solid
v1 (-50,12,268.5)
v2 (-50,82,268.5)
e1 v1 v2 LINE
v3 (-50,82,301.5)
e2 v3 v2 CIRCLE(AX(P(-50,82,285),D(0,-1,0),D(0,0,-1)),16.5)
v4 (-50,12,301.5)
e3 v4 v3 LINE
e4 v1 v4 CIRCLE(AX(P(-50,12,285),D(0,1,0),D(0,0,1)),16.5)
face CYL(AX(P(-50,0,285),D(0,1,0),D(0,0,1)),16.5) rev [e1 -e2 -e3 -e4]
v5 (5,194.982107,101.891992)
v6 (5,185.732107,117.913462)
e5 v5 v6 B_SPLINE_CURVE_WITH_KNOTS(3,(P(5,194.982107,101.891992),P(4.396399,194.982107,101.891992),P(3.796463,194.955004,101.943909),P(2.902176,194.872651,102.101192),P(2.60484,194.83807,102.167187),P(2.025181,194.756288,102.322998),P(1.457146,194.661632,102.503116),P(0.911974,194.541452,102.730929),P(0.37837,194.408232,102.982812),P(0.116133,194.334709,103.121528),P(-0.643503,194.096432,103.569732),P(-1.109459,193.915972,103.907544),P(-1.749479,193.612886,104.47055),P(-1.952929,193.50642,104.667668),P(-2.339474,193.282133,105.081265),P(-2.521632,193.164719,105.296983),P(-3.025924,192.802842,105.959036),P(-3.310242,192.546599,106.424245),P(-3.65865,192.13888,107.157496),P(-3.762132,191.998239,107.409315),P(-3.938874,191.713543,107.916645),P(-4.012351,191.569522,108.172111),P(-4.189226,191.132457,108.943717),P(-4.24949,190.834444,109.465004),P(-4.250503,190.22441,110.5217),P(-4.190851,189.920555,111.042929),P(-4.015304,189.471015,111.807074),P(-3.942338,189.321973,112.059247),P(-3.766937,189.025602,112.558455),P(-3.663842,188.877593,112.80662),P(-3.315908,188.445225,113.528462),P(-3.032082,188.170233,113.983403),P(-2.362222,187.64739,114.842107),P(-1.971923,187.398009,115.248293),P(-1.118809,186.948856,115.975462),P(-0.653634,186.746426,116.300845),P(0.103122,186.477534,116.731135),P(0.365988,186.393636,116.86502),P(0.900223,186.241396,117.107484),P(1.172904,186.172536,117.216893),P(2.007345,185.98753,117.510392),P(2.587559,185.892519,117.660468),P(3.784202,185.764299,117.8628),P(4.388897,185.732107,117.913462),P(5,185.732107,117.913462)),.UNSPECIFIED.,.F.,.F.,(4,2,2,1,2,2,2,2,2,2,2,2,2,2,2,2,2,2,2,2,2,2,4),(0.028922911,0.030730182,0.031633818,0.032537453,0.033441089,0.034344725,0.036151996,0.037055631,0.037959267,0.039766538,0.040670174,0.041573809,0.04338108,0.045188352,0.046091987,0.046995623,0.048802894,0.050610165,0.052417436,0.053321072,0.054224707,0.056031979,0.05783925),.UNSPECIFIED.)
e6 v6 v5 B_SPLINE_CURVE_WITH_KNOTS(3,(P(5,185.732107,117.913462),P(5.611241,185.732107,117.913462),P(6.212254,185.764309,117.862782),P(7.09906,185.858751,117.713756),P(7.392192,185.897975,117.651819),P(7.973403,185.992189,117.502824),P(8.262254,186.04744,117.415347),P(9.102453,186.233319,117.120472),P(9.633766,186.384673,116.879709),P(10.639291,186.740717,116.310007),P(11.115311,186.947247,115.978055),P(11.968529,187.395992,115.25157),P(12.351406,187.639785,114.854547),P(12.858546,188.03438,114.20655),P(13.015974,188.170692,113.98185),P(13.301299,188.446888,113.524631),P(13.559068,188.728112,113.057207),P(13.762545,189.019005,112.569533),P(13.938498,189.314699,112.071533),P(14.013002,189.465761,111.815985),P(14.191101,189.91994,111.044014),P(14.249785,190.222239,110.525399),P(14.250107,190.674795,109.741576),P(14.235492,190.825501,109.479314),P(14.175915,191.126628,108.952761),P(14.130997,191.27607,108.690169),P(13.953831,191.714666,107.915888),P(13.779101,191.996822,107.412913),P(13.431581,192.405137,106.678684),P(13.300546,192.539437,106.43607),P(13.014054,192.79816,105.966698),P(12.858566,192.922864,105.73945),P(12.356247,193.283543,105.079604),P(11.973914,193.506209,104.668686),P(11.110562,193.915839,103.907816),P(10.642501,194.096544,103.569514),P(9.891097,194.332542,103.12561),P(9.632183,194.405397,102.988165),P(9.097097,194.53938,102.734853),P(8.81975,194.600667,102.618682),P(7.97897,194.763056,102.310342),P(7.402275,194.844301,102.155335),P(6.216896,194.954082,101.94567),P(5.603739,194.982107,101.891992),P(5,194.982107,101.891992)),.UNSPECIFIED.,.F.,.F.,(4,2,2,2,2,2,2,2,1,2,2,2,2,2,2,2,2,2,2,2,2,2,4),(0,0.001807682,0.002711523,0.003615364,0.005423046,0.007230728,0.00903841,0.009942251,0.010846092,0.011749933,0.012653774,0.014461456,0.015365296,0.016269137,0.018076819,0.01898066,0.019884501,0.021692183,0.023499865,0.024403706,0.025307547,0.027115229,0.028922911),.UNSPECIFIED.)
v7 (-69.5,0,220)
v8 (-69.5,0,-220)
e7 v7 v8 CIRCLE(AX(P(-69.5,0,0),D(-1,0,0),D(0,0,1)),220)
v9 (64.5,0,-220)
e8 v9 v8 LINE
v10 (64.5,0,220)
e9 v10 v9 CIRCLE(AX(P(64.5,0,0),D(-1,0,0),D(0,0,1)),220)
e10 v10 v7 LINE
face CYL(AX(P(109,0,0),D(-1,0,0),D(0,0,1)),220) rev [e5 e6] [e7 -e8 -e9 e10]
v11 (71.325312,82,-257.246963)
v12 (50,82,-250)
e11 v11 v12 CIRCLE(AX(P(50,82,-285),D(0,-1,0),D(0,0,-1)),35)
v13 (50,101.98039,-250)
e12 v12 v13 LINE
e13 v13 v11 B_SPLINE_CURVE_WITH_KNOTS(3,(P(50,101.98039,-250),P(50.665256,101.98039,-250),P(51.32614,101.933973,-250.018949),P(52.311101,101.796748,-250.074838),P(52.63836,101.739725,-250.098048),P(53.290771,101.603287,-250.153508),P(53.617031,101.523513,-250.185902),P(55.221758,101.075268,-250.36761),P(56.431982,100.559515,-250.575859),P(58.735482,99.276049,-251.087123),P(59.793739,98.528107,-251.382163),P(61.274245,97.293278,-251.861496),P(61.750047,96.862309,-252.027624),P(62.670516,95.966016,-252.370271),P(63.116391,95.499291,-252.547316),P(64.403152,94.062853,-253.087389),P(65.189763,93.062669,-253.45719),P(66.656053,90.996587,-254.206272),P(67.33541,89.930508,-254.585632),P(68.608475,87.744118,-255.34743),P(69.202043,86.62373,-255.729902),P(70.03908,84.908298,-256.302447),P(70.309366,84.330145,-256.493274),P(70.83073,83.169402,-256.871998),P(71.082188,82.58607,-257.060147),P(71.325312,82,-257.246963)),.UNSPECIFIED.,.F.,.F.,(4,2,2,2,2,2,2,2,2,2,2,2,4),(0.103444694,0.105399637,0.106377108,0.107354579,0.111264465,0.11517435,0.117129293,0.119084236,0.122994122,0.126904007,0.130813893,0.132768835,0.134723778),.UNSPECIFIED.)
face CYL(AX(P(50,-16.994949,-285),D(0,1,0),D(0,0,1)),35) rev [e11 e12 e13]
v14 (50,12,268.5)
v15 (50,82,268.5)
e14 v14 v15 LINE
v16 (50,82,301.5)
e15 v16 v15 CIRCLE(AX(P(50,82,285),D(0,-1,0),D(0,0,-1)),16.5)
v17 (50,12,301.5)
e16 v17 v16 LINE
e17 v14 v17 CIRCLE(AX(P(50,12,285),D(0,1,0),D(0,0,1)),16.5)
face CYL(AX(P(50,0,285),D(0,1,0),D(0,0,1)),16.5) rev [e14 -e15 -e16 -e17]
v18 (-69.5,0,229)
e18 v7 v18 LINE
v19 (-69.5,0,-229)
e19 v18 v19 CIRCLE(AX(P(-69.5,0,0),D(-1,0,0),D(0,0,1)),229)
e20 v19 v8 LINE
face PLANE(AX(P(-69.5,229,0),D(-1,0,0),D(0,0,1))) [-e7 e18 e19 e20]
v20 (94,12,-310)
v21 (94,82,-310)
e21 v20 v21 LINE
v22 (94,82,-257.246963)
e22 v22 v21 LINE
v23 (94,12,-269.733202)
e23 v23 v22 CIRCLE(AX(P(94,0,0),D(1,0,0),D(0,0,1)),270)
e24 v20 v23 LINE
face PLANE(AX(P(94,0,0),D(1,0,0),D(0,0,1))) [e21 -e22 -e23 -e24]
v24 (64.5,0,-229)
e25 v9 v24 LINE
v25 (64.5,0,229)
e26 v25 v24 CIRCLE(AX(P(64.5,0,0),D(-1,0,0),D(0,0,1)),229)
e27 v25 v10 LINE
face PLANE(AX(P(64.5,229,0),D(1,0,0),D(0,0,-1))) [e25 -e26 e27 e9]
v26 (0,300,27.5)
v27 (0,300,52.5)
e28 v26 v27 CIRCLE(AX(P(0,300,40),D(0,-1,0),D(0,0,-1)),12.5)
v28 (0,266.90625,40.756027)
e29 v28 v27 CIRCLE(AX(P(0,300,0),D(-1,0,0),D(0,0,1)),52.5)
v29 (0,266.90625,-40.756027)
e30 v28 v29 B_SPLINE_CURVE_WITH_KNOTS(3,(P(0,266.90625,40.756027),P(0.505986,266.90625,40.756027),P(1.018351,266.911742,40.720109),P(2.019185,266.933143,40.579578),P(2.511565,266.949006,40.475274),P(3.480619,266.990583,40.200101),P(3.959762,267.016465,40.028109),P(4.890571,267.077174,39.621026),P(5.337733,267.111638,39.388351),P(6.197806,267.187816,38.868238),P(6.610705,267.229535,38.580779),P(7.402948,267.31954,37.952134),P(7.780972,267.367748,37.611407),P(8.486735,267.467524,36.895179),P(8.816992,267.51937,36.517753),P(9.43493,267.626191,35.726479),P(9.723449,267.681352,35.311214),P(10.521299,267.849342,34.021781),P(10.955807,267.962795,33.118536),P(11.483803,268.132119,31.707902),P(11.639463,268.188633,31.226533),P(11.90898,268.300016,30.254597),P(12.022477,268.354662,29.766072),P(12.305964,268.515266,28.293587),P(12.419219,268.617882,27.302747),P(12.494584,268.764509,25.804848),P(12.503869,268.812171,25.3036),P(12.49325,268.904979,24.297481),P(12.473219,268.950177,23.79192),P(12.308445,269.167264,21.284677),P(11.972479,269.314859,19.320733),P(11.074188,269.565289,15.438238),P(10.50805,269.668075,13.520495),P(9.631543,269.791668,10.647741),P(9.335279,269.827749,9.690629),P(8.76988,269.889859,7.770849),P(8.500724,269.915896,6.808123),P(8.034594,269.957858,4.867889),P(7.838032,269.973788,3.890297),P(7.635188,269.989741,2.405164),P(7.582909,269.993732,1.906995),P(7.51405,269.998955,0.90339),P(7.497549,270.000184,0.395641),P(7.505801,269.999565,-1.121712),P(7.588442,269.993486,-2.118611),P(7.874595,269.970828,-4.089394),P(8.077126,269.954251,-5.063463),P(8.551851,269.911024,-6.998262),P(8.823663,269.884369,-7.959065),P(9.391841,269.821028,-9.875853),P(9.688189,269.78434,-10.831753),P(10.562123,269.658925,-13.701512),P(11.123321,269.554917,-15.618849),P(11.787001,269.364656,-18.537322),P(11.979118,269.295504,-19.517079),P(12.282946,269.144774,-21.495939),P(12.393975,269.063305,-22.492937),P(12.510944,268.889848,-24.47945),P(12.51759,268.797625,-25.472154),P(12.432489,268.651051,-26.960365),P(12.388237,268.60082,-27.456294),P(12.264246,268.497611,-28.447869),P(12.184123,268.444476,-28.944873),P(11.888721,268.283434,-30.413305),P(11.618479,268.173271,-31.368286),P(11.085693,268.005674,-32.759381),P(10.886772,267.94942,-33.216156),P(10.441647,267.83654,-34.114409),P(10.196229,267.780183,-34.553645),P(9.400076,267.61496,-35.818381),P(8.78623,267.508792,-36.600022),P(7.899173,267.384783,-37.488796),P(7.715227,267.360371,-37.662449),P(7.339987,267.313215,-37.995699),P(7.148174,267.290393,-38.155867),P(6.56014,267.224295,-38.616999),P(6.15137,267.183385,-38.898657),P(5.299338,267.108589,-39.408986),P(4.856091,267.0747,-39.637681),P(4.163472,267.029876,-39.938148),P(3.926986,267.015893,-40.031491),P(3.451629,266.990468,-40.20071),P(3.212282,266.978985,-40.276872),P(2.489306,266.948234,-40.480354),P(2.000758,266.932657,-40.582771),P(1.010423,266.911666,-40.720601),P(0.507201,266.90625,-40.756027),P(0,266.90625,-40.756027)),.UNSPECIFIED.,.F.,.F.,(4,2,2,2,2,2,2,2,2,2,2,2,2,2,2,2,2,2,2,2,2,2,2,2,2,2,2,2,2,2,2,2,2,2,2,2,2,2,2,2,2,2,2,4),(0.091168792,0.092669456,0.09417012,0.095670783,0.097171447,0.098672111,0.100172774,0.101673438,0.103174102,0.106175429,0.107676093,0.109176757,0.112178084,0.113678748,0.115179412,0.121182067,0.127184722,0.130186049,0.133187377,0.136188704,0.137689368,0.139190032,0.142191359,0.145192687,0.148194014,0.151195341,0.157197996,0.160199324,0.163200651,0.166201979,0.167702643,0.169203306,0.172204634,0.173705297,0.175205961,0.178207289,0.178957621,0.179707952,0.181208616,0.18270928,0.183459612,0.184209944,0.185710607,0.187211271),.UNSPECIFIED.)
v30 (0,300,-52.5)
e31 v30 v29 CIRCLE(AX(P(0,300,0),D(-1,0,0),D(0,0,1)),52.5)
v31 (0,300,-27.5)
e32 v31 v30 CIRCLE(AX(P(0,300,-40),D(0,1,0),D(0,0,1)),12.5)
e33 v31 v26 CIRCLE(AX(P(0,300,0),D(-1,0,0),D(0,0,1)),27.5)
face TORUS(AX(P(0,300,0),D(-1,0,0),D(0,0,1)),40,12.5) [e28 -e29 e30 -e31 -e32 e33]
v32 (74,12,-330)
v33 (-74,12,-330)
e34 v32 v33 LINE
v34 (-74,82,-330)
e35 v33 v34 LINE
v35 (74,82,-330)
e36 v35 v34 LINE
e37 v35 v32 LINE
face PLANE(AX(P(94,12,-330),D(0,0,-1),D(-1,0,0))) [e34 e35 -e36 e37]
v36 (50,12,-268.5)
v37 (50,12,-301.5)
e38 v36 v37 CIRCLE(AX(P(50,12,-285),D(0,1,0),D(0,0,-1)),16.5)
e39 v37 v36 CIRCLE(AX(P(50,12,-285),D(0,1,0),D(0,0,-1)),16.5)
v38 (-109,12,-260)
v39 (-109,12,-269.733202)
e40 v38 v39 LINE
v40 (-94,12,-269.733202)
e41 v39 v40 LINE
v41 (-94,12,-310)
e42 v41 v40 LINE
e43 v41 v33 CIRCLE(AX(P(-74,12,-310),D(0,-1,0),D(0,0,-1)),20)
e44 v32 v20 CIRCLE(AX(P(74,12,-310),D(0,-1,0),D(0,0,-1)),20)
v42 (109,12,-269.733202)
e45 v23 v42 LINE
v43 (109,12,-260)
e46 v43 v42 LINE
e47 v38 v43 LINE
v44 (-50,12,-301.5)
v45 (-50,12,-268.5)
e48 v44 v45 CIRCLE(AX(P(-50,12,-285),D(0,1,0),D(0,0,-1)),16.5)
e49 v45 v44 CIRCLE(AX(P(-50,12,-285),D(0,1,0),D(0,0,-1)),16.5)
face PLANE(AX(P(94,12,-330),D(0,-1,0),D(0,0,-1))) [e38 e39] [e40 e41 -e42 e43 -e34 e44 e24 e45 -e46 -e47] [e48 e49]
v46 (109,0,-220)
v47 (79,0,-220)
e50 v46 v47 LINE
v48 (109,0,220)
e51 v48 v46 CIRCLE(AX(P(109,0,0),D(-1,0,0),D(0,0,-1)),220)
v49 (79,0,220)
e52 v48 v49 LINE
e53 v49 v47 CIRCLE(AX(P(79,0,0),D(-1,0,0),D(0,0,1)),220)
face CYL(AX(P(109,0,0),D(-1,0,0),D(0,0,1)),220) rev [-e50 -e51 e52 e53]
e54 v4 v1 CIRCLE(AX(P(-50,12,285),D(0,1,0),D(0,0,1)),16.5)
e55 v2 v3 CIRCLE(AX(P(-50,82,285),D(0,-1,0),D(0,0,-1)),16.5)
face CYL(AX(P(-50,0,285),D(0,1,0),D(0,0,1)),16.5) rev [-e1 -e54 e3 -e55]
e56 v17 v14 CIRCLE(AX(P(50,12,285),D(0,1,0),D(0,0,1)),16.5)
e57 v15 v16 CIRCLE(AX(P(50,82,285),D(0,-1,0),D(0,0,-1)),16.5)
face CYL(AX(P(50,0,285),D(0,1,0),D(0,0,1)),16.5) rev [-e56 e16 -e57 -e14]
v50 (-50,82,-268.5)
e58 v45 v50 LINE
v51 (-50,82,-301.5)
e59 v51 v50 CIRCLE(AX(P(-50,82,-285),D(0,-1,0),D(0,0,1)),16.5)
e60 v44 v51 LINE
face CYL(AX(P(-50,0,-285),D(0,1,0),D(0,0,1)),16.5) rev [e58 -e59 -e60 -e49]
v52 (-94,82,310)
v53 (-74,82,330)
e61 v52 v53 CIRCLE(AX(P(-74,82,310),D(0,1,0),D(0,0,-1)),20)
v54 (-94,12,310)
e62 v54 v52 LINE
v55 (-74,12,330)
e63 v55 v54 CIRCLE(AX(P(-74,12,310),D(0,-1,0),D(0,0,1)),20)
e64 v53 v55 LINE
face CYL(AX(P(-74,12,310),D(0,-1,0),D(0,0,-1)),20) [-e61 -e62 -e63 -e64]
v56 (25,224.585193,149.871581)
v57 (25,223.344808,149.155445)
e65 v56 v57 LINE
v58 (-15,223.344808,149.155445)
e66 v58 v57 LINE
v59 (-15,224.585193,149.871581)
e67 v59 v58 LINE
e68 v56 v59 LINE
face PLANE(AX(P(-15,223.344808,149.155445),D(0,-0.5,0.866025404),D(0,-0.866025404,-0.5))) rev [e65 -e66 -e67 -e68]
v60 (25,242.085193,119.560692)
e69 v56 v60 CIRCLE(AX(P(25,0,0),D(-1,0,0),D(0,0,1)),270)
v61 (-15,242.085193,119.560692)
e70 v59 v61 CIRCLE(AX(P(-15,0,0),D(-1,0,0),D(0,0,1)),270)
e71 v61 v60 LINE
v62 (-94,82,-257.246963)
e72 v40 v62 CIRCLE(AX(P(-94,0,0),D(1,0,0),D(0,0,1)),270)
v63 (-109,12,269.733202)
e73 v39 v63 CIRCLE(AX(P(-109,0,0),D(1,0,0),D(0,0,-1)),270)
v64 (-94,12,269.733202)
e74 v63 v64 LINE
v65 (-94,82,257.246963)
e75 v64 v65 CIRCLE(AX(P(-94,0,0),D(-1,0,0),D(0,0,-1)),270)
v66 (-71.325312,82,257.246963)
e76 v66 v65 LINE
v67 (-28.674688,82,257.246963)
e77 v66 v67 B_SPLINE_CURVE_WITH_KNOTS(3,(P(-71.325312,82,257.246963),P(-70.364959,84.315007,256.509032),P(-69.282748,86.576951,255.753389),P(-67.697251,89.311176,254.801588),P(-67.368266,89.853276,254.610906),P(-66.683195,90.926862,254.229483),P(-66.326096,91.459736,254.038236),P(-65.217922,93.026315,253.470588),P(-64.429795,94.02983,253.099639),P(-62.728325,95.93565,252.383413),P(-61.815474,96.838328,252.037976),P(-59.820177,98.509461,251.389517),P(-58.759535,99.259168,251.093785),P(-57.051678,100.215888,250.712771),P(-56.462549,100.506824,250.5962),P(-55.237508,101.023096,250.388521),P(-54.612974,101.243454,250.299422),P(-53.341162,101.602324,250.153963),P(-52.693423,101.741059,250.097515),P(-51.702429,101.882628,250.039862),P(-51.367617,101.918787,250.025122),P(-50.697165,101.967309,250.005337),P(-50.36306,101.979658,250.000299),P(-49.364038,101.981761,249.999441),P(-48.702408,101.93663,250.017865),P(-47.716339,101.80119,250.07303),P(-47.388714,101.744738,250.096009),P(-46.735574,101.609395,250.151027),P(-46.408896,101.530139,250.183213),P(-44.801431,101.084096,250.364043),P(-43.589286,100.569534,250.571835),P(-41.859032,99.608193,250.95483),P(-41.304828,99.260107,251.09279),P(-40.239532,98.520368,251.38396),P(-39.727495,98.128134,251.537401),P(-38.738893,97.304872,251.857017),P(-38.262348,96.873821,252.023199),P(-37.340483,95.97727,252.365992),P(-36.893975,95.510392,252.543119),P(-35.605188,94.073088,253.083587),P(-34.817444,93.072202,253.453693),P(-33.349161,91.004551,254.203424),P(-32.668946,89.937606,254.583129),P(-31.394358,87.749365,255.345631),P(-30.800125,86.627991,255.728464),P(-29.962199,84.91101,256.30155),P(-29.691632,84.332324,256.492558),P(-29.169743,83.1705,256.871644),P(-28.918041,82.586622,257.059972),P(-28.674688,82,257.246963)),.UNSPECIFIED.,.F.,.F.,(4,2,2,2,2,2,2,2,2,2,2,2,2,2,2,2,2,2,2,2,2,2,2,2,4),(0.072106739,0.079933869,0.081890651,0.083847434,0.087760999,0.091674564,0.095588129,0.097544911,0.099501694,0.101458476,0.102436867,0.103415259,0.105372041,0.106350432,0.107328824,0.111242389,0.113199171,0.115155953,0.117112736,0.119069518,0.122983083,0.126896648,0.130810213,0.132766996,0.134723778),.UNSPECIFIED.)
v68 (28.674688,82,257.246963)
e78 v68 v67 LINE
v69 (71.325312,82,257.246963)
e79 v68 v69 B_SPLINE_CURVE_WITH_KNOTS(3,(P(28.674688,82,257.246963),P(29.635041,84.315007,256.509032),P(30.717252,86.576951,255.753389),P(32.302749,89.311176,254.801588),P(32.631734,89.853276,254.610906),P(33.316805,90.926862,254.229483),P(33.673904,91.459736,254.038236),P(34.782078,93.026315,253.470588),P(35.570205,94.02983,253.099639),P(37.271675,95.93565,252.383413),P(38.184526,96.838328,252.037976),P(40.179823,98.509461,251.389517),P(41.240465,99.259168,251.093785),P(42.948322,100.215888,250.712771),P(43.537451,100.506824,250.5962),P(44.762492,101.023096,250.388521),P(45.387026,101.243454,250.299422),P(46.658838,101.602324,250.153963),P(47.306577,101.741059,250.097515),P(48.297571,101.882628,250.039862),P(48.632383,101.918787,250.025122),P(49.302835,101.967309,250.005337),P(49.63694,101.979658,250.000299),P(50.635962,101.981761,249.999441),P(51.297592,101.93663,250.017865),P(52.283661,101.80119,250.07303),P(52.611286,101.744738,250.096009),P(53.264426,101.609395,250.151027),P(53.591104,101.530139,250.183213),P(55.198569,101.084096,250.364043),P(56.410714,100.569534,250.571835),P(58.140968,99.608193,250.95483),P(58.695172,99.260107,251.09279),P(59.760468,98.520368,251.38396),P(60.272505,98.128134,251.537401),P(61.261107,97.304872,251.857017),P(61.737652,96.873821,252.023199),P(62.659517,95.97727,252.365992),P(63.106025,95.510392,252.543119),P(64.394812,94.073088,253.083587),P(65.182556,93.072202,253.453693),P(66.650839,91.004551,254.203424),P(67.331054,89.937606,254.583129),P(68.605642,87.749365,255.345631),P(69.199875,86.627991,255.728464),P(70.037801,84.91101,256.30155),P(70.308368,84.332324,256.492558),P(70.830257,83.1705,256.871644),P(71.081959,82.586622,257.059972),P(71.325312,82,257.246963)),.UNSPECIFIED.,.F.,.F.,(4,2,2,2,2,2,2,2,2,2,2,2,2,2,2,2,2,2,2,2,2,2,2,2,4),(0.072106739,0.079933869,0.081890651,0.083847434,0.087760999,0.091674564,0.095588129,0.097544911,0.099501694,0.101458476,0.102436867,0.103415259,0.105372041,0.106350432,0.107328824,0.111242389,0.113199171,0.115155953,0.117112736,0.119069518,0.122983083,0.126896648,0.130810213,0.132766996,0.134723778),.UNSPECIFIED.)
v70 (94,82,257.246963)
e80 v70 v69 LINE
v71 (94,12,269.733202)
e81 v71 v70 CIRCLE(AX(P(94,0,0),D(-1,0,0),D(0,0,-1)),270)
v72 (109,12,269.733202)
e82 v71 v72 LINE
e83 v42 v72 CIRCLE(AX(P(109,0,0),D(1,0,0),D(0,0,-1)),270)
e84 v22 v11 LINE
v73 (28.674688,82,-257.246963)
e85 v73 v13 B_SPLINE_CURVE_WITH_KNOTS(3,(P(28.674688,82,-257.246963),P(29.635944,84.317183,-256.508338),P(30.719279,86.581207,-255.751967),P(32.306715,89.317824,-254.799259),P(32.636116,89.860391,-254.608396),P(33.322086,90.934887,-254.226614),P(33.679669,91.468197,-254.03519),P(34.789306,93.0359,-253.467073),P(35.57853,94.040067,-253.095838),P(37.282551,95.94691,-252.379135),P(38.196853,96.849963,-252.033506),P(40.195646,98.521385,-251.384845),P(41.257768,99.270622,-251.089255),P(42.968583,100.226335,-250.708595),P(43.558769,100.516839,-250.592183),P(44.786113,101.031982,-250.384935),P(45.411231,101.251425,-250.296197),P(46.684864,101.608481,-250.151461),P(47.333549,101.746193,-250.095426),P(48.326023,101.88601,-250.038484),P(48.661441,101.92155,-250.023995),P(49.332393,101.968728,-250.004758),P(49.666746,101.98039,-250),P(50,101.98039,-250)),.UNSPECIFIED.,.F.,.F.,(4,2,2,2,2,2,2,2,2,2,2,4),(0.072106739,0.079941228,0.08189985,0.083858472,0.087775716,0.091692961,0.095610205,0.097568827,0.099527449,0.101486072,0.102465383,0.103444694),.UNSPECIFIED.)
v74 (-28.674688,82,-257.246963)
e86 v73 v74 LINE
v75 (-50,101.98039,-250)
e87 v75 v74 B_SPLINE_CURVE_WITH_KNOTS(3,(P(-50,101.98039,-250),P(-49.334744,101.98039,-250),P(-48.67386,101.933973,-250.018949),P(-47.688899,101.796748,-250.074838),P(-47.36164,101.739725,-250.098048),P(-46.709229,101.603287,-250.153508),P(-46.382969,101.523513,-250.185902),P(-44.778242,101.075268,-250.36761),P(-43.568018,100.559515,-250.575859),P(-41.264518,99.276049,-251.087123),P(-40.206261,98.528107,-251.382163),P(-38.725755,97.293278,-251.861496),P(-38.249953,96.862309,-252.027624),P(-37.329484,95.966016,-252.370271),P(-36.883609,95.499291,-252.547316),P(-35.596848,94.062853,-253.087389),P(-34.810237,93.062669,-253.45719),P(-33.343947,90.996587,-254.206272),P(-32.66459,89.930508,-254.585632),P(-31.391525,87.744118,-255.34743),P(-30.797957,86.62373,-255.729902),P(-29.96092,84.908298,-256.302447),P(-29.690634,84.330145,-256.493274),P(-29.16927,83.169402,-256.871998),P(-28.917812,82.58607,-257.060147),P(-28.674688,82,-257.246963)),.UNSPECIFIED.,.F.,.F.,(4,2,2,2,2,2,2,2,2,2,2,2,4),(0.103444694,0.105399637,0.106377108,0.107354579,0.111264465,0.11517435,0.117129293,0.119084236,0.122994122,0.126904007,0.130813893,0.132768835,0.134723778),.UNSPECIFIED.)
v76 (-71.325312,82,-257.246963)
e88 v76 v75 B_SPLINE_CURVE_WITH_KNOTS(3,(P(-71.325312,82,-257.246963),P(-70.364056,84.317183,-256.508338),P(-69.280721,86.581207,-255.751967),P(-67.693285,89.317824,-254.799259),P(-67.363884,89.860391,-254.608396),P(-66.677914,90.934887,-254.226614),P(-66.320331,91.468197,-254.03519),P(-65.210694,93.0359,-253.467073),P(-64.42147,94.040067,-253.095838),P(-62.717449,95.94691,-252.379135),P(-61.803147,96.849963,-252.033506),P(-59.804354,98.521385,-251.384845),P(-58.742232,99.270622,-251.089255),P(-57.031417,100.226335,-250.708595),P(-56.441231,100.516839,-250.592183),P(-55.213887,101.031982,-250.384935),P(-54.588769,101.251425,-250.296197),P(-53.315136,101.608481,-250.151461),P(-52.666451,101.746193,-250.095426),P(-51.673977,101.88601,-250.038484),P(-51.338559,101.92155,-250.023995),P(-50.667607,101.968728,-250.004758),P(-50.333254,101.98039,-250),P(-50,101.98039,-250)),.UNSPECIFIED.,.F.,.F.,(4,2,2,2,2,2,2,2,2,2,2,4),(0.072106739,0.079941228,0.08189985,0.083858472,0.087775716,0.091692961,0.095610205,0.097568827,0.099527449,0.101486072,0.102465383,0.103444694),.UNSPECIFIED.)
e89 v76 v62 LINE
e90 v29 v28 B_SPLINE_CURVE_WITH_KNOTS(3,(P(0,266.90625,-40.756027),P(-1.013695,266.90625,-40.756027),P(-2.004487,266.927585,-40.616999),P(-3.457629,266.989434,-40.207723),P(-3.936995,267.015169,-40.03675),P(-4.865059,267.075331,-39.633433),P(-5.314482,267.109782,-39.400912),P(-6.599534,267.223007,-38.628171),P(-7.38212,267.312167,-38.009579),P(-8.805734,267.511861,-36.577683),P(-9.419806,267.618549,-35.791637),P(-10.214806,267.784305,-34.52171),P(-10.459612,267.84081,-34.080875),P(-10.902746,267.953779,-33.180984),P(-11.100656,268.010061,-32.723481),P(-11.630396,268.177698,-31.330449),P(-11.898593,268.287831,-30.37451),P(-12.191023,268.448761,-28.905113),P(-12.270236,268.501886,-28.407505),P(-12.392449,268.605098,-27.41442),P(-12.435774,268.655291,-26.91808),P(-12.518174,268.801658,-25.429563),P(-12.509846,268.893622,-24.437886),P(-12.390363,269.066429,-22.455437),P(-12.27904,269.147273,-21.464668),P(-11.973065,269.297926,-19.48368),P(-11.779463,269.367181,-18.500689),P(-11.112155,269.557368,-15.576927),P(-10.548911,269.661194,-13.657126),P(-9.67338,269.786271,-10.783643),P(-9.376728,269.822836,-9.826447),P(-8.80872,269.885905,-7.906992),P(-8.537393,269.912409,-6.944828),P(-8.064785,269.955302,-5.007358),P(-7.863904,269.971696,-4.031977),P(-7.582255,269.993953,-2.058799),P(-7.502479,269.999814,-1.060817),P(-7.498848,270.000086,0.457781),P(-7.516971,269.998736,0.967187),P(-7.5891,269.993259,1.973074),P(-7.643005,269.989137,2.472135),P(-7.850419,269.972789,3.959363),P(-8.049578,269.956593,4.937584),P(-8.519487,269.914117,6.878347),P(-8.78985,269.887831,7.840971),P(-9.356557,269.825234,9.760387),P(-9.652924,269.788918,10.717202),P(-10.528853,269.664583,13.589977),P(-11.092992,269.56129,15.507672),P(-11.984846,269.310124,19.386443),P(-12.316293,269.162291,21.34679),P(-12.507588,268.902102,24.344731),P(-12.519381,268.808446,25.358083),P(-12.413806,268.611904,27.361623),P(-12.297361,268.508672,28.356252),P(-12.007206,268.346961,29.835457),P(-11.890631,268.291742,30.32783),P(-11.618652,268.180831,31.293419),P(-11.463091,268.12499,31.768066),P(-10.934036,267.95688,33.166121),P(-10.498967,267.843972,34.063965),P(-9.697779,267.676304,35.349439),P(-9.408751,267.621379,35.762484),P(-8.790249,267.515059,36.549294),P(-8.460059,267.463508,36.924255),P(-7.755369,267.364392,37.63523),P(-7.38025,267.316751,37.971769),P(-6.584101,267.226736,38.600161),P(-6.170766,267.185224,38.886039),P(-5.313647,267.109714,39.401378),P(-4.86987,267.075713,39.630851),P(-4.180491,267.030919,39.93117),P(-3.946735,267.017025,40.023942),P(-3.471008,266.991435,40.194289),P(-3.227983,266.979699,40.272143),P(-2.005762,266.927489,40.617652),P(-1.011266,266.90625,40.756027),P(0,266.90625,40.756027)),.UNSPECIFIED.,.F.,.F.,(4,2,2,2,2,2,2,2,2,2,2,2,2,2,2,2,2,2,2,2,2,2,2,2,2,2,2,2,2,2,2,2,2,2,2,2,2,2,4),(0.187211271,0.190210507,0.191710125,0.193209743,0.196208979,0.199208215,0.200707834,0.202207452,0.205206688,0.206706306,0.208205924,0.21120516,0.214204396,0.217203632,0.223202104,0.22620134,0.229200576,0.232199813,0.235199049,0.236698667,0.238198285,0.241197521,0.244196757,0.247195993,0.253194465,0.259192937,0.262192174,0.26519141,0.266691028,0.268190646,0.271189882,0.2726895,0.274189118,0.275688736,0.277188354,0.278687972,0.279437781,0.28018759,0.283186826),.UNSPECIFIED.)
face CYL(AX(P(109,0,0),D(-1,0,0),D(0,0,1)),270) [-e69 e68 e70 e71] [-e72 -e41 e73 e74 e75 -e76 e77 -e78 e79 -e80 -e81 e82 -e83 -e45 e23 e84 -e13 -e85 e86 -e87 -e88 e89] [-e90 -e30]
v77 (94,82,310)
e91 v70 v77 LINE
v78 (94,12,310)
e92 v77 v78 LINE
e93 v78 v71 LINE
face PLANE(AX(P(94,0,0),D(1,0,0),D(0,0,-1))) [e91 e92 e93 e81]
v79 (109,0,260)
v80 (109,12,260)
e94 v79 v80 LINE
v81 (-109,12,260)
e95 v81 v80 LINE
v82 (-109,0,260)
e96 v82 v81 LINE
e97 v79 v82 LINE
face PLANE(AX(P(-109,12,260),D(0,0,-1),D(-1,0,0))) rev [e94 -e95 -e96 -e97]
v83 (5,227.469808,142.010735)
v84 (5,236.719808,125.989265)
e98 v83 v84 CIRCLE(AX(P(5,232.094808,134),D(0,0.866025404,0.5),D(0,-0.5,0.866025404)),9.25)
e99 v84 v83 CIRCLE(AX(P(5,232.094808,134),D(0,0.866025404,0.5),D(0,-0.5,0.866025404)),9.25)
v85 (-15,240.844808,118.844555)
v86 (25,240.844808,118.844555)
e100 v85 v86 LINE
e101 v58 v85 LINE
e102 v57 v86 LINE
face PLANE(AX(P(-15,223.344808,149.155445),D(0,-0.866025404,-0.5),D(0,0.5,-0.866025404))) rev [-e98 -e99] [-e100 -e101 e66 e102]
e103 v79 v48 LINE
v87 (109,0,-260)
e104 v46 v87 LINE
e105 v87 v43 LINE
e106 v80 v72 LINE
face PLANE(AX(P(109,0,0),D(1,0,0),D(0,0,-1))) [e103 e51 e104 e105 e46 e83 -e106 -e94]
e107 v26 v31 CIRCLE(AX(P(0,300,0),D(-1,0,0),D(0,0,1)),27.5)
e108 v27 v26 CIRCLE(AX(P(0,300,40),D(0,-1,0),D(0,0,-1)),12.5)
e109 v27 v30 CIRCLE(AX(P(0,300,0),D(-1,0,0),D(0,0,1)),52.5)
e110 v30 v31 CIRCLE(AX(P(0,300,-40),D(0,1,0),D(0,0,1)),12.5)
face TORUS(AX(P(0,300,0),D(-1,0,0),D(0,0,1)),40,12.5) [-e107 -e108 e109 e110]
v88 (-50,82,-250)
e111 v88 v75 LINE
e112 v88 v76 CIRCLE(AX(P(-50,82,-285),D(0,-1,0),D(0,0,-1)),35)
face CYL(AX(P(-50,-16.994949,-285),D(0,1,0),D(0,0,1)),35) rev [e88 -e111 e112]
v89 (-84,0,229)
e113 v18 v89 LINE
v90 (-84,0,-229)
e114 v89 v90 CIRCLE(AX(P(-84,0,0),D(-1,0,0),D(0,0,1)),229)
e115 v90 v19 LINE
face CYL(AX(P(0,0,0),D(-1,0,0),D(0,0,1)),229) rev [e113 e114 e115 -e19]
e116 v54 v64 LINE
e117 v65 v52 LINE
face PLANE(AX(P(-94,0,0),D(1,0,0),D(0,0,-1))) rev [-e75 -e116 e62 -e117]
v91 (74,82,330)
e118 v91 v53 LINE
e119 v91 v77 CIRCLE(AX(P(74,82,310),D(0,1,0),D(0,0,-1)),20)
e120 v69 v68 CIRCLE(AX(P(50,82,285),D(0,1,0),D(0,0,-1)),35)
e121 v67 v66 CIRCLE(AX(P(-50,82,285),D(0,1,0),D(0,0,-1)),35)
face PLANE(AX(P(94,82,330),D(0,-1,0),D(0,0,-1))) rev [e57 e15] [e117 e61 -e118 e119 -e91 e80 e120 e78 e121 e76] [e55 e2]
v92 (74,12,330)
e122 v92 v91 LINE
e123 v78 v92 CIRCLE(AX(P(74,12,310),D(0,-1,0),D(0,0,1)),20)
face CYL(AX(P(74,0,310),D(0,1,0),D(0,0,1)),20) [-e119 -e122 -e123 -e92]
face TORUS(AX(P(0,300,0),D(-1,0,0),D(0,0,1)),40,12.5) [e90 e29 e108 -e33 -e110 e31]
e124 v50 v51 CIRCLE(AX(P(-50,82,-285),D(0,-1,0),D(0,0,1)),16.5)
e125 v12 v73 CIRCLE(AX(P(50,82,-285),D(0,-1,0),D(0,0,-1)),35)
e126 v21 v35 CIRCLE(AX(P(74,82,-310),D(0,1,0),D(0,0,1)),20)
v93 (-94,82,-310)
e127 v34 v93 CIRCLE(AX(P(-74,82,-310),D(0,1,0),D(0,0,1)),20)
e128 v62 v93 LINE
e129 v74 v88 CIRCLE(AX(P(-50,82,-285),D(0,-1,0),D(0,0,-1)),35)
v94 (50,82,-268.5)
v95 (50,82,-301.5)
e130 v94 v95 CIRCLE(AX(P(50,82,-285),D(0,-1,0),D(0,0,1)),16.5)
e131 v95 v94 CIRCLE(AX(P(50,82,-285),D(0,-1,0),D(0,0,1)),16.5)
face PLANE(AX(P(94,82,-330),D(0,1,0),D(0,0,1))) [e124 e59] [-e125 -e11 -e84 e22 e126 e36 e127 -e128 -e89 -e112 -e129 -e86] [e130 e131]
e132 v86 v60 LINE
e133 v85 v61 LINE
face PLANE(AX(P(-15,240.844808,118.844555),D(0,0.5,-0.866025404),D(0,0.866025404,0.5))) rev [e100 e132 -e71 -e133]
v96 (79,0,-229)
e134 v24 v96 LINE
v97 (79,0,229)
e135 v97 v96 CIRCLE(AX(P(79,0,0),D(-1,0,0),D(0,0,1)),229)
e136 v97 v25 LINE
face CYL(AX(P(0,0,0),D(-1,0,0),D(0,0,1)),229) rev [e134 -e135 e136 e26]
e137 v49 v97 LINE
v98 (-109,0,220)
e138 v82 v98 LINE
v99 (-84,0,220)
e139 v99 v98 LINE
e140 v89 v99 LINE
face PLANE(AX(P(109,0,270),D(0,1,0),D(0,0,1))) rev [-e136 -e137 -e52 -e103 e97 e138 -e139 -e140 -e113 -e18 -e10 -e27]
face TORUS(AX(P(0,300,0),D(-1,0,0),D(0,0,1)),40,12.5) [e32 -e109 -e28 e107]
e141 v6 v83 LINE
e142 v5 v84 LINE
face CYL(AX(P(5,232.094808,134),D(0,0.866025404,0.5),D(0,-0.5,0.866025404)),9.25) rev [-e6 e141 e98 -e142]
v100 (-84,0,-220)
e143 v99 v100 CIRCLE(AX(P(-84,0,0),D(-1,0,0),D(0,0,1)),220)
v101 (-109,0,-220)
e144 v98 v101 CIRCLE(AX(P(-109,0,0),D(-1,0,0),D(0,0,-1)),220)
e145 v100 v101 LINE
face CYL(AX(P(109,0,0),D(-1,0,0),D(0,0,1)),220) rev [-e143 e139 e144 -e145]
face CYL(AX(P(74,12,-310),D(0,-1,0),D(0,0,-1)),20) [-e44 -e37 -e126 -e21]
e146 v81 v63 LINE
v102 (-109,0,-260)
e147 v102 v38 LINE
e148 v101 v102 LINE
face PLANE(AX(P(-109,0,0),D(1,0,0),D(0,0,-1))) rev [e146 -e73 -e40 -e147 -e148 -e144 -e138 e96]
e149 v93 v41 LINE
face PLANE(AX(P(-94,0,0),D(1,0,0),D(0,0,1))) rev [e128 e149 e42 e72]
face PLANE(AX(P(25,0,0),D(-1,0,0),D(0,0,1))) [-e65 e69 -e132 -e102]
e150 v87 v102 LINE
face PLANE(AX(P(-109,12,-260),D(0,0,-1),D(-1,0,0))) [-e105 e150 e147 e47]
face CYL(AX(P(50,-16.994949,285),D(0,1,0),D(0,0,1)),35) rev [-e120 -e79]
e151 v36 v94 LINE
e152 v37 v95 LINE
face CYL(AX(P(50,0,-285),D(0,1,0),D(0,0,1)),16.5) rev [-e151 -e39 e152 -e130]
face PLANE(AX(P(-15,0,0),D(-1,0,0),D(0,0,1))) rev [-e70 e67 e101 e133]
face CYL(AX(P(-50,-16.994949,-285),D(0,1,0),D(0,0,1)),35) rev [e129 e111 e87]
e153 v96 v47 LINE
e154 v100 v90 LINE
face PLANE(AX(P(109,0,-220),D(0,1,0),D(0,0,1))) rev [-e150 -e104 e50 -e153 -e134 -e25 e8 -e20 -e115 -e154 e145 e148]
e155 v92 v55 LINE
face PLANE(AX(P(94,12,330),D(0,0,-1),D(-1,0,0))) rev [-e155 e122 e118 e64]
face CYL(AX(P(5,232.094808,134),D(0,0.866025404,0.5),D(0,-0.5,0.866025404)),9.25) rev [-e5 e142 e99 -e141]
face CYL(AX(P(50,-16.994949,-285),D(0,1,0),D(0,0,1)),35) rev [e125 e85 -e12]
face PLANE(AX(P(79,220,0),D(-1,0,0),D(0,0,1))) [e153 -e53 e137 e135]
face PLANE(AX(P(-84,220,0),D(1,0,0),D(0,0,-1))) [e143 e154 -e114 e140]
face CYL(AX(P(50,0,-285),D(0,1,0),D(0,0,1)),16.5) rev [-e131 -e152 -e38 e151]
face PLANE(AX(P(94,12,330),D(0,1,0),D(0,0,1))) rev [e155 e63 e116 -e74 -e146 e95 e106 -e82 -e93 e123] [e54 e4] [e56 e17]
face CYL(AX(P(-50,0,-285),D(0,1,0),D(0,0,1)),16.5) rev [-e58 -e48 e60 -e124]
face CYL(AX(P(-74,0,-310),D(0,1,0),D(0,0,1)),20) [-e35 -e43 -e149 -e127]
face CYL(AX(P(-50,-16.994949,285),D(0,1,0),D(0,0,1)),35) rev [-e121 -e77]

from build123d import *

# Parameters (mm, degrees)
BOSS_EXTRUDE2_DEPTH    = 109
BOSS_EXTRUDE3_DEPTH    = 94
SKETCH5_R              = 16.5
CUT_EXTRUDE1_DEPTH     = 396.126562003
CUT_EXTRUDE2_START     = 82
SKETCH6_R              = 35
CUT_EXTRUDE2_DEPTH     = 19.98039
SKETCH7_W              = 39.278789695
SKETCH7_H              = 17.735547429
CUT_EXTRUDE3_DEPTH     = 441.092035915
FILLET1_R              = 20
FILLET1_OF_MIRROR1_R   = 20
SKETCH8_W              = 14.5
SKETCH8_H              = 9
SKETCH9_R              = 12.5
CUT_EXTRUDE4_START     = 5
CUT_EXTRUDE4_DEPTH     = 20
M20X1_5_TAPPED_HOLE1_D = 18.5


with BuildPart() as part:
    # Sketch1 → Boss-Extrude2 (new, symmetric)
    with BuildSketch(Plane(origin=(0, 0, 0), x_dir=(0, 0, -1), z_dir=(1, 0, 0))):
        with BuildLine():
            Line((-270, 0), (-220, 0))
            ThreePointArc((-220, 0), (0, 220), (220, 0))
            Line((220, 0), (270, 0))
            ThreePointArc((270, 0), (0, 270), (-270, 0))
        make_face()
    extrude(amount=BOSS_EXTRUDE2_DEPTH, both=True)

    # Sketch4 → Boss-Extrude3 (add, symmetric)
    with BuildSketch(Plane(origin=(0, 0, 0), x_dir=(0, 0, -1), z_dir=(1, 0, 0))):
        with BuildLine():
            Line((-330, 12), (-269.733201516, 12))
            ThreePointArc((-269.733201516, 12), (-265.804483526, 47.41283094), (-257.246963053, 82))
            Line((-257.246963053, 82), (-330, 82))
            Line((-330, 82), (-330, 12))
        make_face()
    boss_extrude3 = extrude(amount=BOSS_EXTRUDE3_DEPTH, both=True)

    # Sketch5 → Cut-Extrude1 (cut, symmetric)
    with BuildSketch(Plane(origin=(0, 82, 0), x_dir=(1, 0, 0), z_dir=(0, 1, 0))):
        with Locations(Location((50, -285, 0), (0, 0, 65.380022671))):
            Circle(SKETCH5_R)
        with Locations(Location((-50, -285, 0), (0, 0, 65.380022671))):
            Circle(SKETCH5_R)
    cut_extrude1 = extrude(amount=CUT_EXTRUDE1_DEPTH, both=True, mode=Mode.SUBTRACT)

    # Sketch6 → Cut-Extrude2 (cut)
    with BuildSketch(Plane(origin=(0, 0, 0), x_dir=(1, 0, 0), z_dir=(0, 1, 0)).offset(CUT_EXTRUDE2_START)):
        with Locations((-50, -285)):
            Circle(SKETCH6_R)
        with Locations((50, -285)):
            Circle(SKETCH6_R)
    cut_extrude2 = extrude(amount=CUT_EXTRUDE2_DEPTH, mode=Mode.SUBTRACT)

    # Sketch7 → Cut-Extrude3 (cut, symmetric)
    with BuildSketch(Plane(origin=(0, 0, 0), x_dir=(0, 0, -1), z_dir=(1, 0, 0))):
        with Locations((-279.639394848, 3.132226285)):
            Rectangle(SKETCH7_W, SKETCH7_H)
    cut_extrude3 = extrude(amount=CUT_EXTRUDE3_DEPTH, both=True, mode=Mode.SUBTRACT)

    # Fillet1
    fillet1_edges = [part.edges().sort_by_distance(p)[0] for p in [
        (-94, 47, 330),
        (94, 47, 330),
    ]]
    fillet(fillet1_edges, radius=FILLET1_R)

    # Mirror1: Boss-Extrude3, Cut-Extrude1, Cut-Extrude2, Cut-Extrude3 across plane
    add(boss_extrude3.mirror(Plane.XY))
    add(cut_extrude1.mirror(Plane.XY), mode=Mode.SUBTRACT)
    add(cut_extrude2.mirror(Plane.XY), mode=Mode.SUBTRACT)
    add(cut_extrude3.mirror(Plane.XY), mode=Mode.SUBTRACT)

    # Fillet1 of Mirror1
    fillet1_of_mirror1_edges = [part.edges().sort_by_distance(p)[0] for p in [
        (-94, 47, -330),
        (94, 47, -330),
    ]]
    fillet(fillet1_of_mirror1_edges, radius=FILLET1_OF_MIRROR1_R)

    # Sketch8 → Cut-Revolve1 (revolve, cut)
    with BuildSketch(Plane.XY):
        with Locations((-76.75, 224.5)):
            Rectangle(SKETCH8_W, SKETCH8_H)
        with Locations((71.75, 224.5)):
            Rectangle(SKETCH8_W, SKETCH8_H)
    revolve(axis=Axis((0, 0, 0), (1, 0, 0)), mode=Mode.SUBTRACT)

    # Sketch9 → Revolve1 (revolve)
    with BuildSketch(Plane.XY, mode=Mode.PRIVATE) as revolve1_sk:
        with Locations((0, 340)):
            Circle(SKETCH9_R)
    revolve(revolve1_sk.sketch.rotate(Axis((0, 300, 0), (1, 0, 0)), 340.461761532), axis=Axis((0, 300, 0), (1, 0, 0)))

    # Sketch10 → Cut-Extrude4 (cut, symmetric)
    with BuildSketch(Plane(origin=(0, 0, 0), x_dir=(0, 0, -1), z_dir=(1, 0, 0)).offset(CUT_EXTRUDE4_START)):
        Polygon((-149.155444566, 223.344808214), (-118.844555434, 240.844808214), (-120.844555434, 244.308909829), (-151.155444566, 226.808909829), align=None)
    extrude(amount=CUT_EXTRUDE4_DEPTH, both=True, mode=Mode.SUBTRACT)

    # M20x1.5 Tapped Hole1 (through all)
    with Locations(Plane(origin=(5, 232.094808214, 134), x_dir=(0, -0.5, 0.866025403784), z_dir=(0, 0.866025403784, 0.5))):
        with Locations((0, 0)):
            Hole(M20X1_5_TAPPED_HOLE1_D / 2)


solid = part.part
